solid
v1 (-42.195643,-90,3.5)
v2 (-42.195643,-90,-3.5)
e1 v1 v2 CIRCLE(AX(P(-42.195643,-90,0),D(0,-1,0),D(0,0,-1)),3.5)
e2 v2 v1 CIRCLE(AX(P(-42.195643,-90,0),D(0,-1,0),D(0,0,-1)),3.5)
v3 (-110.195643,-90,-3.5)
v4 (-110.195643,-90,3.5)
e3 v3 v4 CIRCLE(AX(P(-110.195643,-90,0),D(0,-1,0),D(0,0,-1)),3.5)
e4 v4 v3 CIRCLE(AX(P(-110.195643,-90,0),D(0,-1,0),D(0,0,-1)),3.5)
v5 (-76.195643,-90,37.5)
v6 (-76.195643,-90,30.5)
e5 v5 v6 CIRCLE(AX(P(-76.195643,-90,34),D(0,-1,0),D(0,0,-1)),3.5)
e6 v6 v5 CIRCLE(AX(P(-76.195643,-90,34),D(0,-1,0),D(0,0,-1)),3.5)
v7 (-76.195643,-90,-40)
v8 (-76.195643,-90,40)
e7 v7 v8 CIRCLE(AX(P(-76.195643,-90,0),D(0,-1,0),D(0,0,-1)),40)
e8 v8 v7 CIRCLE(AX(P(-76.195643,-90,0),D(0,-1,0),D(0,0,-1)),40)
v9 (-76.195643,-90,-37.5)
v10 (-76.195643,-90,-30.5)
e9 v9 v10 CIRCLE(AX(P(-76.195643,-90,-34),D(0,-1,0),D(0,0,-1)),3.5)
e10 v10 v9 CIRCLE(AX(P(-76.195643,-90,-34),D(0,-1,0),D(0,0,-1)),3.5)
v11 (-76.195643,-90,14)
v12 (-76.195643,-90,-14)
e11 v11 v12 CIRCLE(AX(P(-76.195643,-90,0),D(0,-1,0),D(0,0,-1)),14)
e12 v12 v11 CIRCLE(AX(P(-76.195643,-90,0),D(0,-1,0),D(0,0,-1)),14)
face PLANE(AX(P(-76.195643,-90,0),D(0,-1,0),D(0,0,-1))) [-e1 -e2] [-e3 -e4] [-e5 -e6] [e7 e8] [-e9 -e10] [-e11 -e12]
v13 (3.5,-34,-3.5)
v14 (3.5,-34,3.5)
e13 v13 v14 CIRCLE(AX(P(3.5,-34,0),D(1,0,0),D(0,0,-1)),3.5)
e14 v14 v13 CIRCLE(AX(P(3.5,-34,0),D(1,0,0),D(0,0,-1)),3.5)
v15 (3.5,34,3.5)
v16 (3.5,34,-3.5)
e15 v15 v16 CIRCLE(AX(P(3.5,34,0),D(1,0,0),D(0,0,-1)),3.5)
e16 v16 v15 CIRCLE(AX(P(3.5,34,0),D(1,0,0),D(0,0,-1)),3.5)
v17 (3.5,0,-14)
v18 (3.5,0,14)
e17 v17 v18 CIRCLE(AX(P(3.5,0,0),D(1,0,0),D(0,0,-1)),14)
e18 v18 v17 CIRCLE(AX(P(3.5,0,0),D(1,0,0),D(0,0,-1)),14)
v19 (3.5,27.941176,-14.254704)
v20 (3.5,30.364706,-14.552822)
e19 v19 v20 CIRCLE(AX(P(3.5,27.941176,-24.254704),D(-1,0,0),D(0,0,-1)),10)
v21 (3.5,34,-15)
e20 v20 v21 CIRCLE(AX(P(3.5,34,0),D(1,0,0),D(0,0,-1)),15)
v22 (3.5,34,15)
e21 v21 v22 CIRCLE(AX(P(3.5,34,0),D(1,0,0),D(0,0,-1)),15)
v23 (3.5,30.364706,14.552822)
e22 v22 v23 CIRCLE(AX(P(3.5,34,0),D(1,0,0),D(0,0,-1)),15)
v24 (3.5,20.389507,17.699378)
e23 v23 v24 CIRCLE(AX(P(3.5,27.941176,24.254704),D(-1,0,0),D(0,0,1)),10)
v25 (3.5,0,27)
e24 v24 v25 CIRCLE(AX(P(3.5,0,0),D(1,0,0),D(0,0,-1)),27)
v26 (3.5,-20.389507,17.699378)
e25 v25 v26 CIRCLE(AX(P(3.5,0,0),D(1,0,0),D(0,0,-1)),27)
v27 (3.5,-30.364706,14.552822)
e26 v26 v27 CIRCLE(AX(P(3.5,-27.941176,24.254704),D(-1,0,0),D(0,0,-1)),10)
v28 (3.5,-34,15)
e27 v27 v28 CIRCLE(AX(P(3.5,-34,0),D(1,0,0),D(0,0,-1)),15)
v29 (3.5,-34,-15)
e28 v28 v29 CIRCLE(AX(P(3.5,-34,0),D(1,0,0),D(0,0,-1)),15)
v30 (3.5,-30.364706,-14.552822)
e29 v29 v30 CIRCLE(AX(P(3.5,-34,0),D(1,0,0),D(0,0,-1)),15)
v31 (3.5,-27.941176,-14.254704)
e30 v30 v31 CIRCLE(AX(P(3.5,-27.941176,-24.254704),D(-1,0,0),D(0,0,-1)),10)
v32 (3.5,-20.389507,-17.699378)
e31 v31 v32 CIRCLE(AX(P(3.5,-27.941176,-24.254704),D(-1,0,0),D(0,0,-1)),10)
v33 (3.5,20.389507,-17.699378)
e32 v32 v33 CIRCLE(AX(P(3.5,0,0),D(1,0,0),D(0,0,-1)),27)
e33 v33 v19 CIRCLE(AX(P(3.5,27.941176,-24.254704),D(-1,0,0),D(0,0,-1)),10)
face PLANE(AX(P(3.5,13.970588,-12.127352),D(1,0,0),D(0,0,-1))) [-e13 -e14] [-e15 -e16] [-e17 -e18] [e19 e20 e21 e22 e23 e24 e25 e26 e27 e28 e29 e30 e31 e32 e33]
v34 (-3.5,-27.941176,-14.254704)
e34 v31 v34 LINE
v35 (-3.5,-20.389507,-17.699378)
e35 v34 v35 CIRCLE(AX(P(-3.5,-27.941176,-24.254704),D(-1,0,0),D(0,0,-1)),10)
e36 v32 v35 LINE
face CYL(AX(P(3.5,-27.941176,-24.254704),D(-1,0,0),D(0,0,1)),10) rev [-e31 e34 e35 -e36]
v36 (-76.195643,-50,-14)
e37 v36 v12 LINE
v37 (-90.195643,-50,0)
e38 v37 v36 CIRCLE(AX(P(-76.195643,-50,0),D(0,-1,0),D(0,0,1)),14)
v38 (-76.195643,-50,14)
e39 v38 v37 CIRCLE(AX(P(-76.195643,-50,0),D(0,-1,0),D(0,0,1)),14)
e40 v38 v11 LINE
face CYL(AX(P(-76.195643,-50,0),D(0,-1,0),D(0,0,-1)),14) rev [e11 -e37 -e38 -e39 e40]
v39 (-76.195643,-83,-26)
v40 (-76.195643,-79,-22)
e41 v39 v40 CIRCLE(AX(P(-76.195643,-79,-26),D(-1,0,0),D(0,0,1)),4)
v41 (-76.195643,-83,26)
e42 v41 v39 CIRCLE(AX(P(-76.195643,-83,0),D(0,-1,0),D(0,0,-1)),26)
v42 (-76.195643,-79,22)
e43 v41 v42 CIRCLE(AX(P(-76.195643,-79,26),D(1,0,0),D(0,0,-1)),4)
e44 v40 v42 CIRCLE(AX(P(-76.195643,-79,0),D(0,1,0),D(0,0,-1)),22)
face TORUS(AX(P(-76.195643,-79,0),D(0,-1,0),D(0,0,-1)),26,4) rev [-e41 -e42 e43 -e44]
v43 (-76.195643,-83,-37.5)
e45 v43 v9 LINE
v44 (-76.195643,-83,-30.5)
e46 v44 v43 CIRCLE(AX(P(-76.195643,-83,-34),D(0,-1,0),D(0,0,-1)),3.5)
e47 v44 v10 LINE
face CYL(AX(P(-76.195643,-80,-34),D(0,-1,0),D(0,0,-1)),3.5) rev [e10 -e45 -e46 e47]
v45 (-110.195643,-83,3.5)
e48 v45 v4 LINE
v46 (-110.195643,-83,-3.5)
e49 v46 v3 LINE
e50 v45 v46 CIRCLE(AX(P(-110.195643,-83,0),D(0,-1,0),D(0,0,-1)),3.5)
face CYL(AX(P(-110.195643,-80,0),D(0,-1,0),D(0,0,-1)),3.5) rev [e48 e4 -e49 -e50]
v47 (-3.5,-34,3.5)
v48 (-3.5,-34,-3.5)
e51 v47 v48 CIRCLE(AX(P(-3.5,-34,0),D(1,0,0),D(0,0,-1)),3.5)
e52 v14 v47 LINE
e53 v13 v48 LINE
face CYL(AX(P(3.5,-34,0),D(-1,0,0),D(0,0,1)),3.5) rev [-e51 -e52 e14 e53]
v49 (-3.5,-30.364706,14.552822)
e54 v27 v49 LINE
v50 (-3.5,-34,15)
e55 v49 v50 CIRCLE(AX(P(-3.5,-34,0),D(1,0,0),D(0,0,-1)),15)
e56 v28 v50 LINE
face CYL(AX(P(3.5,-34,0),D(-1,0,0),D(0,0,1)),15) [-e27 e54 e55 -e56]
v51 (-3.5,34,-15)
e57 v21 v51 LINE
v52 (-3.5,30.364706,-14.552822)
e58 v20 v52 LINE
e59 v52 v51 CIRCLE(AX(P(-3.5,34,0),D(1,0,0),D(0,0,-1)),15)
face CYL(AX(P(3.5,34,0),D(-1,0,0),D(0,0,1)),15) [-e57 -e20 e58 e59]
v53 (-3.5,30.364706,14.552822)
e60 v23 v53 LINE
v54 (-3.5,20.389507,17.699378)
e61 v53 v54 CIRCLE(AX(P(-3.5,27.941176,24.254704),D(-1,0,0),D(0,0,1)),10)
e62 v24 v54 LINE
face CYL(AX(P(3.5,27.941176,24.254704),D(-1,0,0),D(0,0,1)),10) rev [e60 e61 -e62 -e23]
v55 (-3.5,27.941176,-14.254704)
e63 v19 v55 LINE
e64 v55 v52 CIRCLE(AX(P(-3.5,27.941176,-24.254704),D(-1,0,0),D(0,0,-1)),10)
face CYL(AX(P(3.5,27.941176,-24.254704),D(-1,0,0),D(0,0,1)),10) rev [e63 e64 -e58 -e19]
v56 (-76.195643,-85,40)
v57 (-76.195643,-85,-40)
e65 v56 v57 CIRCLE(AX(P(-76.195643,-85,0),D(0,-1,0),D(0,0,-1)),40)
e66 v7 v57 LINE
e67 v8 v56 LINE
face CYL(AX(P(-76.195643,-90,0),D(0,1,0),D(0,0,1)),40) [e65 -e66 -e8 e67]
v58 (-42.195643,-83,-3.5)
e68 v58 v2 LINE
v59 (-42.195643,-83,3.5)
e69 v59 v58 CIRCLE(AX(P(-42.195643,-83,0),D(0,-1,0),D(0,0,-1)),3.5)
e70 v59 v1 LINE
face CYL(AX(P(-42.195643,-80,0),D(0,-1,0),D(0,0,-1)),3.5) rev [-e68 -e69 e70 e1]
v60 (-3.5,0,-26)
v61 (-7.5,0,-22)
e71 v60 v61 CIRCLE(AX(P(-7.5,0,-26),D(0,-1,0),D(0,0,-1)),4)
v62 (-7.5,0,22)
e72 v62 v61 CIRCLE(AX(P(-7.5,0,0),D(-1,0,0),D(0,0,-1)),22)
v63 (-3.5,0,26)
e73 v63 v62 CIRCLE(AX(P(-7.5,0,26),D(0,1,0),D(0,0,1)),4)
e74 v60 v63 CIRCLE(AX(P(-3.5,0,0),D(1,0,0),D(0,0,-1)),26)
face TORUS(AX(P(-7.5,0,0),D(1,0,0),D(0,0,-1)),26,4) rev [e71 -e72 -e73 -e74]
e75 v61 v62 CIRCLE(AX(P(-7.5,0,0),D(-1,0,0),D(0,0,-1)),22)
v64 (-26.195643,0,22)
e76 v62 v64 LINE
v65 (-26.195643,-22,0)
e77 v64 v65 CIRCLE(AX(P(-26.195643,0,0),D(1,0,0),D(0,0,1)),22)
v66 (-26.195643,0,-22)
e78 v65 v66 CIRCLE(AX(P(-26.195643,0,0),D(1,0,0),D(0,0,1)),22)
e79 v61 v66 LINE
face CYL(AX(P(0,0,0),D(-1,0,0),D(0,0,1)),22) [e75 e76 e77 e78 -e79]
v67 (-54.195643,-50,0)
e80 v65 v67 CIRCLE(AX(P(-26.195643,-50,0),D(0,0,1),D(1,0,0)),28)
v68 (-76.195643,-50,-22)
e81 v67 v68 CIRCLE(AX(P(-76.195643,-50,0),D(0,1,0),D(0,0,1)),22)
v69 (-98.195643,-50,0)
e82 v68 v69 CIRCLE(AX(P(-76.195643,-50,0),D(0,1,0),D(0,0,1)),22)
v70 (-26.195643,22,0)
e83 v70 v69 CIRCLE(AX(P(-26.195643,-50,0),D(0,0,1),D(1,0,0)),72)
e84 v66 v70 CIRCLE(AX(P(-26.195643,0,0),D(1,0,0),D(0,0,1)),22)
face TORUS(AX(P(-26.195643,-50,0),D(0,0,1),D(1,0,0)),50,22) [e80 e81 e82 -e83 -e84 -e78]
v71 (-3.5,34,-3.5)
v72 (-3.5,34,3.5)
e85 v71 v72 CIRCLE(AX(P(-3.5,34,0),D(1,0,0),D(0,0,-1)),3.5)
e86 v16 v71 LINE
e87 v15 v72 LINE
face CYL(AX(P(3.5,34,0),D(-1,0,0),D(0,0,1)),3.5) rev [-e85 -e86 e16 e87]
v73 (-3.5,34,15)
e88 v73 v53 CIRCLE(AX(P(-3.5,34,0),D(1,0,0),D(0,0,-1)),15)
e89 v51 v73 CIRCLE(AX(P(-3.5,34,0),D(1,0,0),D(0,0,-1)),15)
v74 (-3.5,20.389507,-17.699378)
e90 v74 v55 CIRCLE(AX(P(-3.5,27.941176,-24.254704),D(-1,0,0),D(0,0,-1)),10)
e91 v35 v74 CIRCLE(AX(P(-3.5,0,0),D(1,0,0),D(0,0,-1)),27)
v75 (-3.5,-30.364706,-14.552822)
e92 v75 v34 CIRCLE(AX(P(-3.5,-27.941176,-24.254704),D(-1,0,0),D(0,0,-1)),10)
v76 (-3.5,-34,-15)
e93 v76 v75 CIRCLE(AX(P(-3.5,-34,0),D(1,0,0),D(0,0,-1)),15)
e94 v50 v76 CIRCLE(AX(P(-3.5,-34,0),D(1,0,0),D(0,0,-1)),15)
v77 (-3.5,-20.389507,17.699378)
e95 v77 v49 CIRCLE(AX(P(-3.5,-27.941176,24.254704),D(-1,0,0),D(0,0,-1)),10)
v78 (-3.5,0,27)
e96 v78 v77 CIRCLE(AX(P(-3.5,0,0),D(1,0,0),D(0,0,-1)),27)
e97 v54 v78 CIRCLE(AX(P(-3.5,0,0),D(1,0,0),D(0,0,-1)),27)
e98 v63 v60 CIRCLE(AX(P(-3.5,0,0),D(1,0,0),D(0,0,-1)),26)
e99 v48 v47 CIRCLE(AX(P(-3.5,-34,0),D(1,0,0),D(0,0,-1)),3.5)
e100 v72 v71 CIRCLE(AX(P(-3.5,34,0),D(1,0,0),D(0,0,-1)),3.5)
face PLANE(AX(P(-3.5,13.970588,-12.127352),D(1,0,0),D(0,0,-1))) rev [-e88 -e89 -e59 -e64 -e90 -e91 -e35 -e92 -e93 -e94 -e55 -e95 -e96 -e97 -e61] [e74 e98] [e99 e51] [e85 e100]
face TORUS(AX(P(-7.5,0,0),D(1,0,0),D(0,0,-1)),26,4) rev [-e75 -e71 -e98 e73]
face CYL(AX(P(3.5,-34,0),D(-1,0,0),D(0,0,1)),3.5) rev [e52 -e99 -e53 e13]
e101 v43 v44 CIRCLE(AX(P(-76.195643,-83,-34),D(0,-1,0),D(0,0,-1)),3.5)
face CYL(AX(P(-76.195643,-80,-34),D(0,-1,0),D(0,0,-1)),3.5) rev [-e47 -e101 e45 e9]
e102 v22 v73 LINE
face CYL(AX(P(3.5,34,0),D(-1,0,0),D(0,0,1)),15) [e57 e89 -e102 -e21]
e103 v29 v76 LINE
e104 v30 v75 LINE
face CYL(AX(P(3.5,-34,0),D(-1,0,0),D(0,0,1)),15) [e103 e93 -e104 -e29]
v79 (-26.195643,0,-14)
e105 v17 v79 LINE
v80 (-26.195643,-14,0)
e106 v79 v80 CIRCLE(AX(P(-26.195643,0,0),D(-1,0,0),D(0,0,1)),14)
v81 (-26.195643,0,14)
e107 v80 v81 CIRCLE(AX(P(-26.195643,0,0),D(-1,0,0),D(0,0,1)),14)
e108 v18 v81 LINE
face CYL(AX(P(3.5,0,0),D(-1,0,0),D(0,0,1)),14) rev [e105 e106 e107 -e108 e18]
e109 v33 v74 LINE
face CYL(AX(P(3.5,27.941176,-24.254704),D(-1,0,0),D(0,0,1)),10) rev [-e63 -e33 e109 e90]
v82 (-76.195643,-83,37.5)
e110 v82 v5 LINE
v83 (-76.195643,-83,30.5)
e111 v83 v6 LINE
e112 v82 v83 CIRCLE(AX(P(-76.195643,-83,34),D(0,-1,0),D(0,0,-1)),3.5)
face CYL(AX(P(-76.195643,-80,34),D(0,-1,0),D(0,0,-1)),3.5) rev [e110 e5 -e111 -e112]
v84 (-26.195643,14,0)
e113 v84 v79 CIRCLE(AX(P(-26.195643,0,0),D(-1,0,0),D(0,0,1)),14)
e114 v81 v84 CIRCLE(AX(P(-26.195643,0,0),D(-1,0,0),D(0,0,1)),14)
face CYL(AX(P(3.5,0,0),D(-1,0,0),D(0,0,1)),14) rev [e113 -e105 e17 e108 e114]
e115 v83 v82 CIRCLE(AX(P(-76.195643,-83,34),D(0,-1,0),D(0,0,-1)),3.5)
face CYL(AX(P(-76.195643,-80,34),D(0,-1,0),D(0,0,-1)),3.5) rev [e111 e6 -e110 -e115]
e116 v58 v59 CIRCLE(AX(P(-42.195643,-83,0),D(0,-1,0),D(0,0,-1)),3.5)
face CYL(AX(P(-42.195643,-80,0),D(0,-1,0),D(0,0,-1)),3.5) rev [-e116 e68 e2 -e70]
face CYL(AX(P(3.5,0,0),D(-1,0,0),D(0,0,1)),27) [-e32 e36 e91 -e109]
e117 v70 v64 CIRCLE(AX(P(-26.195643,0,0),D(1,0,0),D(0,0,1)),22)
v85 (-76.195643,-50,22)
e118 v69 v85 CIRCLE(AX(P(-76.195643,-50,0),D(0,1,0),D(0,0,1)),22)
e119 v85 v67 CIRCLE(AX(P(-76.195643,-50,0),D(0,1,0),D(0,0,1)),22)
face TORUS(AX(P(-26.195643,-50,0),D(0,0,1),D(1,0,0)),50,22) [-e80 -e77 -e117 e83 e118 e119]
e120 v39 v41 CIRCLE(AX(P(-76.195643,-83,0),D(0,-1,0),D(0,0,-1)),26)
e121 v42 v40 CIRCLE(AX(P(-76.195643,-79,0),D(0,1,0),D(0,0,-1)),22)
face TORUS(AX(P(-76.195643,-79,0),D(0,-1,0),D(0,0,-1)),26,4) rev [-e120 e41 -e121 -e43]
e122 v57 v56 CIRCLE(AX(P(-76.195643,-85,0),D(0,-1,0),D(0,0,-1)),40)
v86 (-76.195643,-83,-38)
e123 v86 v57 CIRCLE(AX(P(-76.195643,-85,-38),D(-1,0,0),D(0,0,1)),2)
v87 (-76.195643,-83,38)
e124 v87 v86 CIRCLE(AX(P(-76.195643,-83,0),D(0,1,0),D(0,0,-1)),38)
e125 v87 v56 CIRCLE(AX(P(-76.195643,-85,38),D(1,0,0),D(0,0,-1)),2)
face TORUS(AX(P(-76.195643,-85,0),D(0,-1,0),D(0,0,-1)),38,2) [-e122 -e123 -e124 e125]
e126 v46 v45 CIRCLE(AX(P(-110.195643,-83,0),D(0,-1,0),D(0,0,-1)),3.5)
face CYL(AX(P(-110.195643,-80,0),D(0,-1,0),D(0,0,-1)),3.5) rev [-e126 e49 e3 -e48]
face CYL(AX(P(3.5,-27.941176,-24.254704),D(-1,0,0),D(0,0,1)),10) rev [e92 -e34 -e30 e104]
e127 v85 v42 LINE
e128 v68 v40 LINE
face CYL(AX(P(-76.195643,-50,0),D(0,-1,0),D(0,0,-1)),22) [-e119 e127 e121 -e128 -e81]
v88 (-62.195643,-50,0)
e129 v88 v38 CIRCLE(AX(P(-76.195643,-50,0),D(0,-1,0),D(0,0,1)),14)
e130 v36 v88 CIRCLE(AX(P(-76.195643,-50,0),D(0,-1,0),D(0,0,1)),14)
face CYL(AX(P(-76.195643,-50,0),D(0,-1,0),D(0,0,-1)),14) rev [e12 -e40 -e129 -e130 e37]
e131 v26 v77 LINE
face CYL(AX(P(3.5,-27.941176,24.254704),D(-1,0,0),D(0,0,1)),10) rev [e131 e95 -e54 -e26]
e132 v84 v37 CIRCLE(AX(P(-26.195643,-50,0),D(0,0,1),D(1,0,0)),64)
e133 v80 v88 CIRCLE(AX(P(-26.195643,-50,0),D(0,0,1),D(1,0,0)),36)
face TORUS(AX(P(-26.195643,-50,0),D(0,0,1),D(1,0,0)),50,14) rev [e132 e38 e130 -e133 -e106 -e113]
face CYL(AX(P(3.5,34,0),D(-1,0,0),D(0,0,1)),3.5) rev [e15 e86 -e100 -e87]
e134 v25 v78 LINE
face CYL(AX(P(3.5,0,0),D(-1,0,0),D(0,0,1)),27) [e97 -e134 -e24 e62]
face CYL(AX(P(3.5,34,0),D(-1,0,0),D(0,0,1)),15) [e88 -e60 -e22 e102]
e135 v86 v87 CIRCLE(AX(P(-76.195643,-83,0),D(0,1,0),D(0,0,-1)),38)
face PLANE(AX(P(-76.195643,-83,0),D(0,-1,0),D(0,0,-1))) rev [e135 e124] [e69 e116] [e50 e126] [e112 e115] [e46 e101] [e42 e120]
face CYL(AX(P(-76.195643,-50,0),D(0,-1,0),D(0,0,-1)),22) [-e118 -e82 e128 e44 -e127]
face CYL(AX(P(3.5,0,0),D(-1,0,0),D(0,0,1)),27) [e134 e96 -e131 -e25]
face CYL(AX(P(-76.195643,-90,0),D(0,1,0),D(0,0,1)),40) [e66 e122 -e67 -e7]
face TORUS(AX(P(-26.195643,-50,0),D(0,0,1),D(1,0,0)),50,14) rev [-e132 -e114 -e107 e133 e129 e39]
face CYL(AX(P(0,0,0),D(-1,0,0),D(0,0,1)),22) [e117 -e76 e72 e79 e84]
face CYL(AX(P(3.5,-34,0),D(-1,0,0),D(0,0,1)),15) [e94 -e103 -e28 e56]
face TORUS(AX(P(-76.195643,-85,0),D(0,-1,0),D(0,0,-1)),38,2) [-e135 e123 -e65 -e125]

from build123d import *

# Parameters (mm, degrees)
OVAL_FLANGE_SKETCH_R               = 14
OVAL_FLANGE_SKETCH_R_2             = 3.5
OVAL_FLANGE_DEPTH                  = 3.5
PIPE_SECTION_SKETCH_44X_28_R       = 22
PIPE_SECTION_SKETCH_44X_28_R_2     = 14
ROUND_START                        = 7
ROUND_FLANGE_SKETCH_R              = 40
ROUND_FLANGE_SKETCH_R_2            = 14
ROUND_FLANGE_80_DEPTH              = 7
PIPE_TO_FLANGE_FILLETS_R4_R        = 4
ROUND_FLANGE_EDGE_FILLET_R2_R      = 2
ROUND_FLANGE_BOLT_HOLES_SKETCH_R   = 3.5
ROUND_FLANGE_BOLT_HOLES_4X_7_DEPTH = 10


with BuildPart() as part:
    # Oval Flange Sketch → Oval Flange (new, symmetric)
    with BuildSketch(Plane(origin=(0, 0, 0), x_dir=(0, 0, -1), z_dir=(1, 0, 0))):
        with BuildLine():
            ThreePointArc((17.699378464, -20.389507154), (27, 0), (17.699378464, 20.389507154))
            ThreePointArc((17.699378464, 20.389507154), (14.717914983, 24.932911413), (14.552822293, 30.364705882))
            ThreePointArc((14.552822293, 30.364705882), (0, 49), (-14.552822293, 30.364705882))
            ThreePointArc((-14.552822293, 30.364705882), (-14.717914983, 24.932911413), (-17.699378464, 20.389507154))
            ThreePointArc((-17.699378464, 20.389507154), (-27, 0), (-17.699378464, -20.389507154))
            ThreePointArc((-17.699378464, -20.389507154), (-14.717914983, -24.932911413), (-14.552822293, -30.364705882))
            ThreePointArc((-14.552822293, -30.364705882), (0, -49), (14.552822293, -30.364705882))
            ThreePointArc((14.552822293, -30.364705882), (14.717914983, -24.932911413), (17.699378464, -20.389507154))
        make_face()
        Circle(OVAL_FLANGE_SKETCH_R, mode=Mode.SUBTRACT)
        with Locations((0, 34)):
            Circle(OVAL_FLANGE_SKETCH_R_2, mode=Mode.SUBTRACT)
        with Locations((0, -34)):
            Circle(OVAL_FLANGE_SKETCH_R_2, mode=Mode.SUBTRACT)
    extrude(amount=OVAL_FLANGE_DEPTH, both=True)

    # Pipe Elbow Sweep: sweep along a path in Elbow Path Sketch
    with BuildLine(Plane.XY) as pipe_elbow_sweep_path:
        Line((0, 0), (-26.195643288, 0))
        ThreePointArc((-26.195643288, 0), (-61.550982347, -14.644660941), (-76.195643288, -50))
        Line((-76.195643288, -50), (-76.195643288, -83))
    # Pipe Section Sketch Ø44xØ28 → Pipe Elbow Sweep (sweep)
    with BuildSketch(Plane(origin=(0, -83, 0), x_dir=(1, 0, 0), z_dir=(0, 1, 0))):
        with Locations((-76.195643288, 0)):
            Circle(PIPE_SECTION_SKETCH_44X_28_R)
        with Locations((-76.195643288, 0)):
            Circle(PIPE_SECTION_SKETCH_44X_28_R_2, mode=Mode.SUBTRACT)
    sweep(path=pipe_elbow_sweep_path.line)

    # Round Flange Sketch → Round Flange Ø80 (add)
    with BuildSketch(Plane.XZ.offset(83).offset(ROUND_START)):
        with Locations(Location((-76.195643288, 0, 0), (0, 0, 270))):
            Circle(ROUND_FLANGE_SKETCH_R)
        with Locations(Location((-76.195643288, 0, 0), (0, 0, 270))):
            Circle(ROUND_FLANGE_SKETCH_R_2, mode=Mode.SUBTRACT)
    extrude(amount=-ROUND_FLANGE_80_DEPTH)

    # Pipe to Flange Fillets R4
    pipe_to_flange_fillets_r4_edges = [part.edges().sort_by_distance(p)[0] for p in [
        (-3.5, 22, 0),
        (-98.195643288, -83, 0),
    ]]
    fillet(pipe_to_flange_fillets_r4_edges, radius=PIPE_TO_FLANGE_FILLETS_R4_R)

    # Round Flange Edge Fillet R2
    round_flange_edge_fillet_r2_edges = [part.edges().sort_by_distance(p)[0] for p in [
        (-76.195643288, -83, 40),
    ]]
    fillet(round_flange_edge_fillet_r2_edges, radius=ROUND_FLANGE_EDGE_FILLET_R2_R)

    # Round Flange Bolt Holes Sketch → Round Flange Bolt Holes 4xØ7 (cut)
    with BuildSketch(Plane.XZ.offset(90)):
        with Locations(Location((-110.195643288, 0, 0), (0, 0, 270))):
            Circle(ROUND_FLANGE_BOLT_HOLES_SKETCH_R)
        with Locations(Location((-42.195643288, 0, 0), (0, 0, 270))):
            Circle(ROUND_FLANGE_BOLT_HOLES_SKETCH_R)
        with Locations(Location((-76.195643288, 34, 0), (0, 0, 270))):
            Circle(ROUND_FLANGE_BOLT_HOLES_SKETCH_R)
        with Locations(Location((-76.195643288, -34, 0), (0, 0, 270))):
            Circle(ROUND_FLANGE_BOLT_HOLES_SKETCH_R)
    extrude(amount=-ROUND_FLANGE_BOLT_HOLES_4X_7_DEPTH, mode=Mode.SUBTRACT)


solid = part.part
